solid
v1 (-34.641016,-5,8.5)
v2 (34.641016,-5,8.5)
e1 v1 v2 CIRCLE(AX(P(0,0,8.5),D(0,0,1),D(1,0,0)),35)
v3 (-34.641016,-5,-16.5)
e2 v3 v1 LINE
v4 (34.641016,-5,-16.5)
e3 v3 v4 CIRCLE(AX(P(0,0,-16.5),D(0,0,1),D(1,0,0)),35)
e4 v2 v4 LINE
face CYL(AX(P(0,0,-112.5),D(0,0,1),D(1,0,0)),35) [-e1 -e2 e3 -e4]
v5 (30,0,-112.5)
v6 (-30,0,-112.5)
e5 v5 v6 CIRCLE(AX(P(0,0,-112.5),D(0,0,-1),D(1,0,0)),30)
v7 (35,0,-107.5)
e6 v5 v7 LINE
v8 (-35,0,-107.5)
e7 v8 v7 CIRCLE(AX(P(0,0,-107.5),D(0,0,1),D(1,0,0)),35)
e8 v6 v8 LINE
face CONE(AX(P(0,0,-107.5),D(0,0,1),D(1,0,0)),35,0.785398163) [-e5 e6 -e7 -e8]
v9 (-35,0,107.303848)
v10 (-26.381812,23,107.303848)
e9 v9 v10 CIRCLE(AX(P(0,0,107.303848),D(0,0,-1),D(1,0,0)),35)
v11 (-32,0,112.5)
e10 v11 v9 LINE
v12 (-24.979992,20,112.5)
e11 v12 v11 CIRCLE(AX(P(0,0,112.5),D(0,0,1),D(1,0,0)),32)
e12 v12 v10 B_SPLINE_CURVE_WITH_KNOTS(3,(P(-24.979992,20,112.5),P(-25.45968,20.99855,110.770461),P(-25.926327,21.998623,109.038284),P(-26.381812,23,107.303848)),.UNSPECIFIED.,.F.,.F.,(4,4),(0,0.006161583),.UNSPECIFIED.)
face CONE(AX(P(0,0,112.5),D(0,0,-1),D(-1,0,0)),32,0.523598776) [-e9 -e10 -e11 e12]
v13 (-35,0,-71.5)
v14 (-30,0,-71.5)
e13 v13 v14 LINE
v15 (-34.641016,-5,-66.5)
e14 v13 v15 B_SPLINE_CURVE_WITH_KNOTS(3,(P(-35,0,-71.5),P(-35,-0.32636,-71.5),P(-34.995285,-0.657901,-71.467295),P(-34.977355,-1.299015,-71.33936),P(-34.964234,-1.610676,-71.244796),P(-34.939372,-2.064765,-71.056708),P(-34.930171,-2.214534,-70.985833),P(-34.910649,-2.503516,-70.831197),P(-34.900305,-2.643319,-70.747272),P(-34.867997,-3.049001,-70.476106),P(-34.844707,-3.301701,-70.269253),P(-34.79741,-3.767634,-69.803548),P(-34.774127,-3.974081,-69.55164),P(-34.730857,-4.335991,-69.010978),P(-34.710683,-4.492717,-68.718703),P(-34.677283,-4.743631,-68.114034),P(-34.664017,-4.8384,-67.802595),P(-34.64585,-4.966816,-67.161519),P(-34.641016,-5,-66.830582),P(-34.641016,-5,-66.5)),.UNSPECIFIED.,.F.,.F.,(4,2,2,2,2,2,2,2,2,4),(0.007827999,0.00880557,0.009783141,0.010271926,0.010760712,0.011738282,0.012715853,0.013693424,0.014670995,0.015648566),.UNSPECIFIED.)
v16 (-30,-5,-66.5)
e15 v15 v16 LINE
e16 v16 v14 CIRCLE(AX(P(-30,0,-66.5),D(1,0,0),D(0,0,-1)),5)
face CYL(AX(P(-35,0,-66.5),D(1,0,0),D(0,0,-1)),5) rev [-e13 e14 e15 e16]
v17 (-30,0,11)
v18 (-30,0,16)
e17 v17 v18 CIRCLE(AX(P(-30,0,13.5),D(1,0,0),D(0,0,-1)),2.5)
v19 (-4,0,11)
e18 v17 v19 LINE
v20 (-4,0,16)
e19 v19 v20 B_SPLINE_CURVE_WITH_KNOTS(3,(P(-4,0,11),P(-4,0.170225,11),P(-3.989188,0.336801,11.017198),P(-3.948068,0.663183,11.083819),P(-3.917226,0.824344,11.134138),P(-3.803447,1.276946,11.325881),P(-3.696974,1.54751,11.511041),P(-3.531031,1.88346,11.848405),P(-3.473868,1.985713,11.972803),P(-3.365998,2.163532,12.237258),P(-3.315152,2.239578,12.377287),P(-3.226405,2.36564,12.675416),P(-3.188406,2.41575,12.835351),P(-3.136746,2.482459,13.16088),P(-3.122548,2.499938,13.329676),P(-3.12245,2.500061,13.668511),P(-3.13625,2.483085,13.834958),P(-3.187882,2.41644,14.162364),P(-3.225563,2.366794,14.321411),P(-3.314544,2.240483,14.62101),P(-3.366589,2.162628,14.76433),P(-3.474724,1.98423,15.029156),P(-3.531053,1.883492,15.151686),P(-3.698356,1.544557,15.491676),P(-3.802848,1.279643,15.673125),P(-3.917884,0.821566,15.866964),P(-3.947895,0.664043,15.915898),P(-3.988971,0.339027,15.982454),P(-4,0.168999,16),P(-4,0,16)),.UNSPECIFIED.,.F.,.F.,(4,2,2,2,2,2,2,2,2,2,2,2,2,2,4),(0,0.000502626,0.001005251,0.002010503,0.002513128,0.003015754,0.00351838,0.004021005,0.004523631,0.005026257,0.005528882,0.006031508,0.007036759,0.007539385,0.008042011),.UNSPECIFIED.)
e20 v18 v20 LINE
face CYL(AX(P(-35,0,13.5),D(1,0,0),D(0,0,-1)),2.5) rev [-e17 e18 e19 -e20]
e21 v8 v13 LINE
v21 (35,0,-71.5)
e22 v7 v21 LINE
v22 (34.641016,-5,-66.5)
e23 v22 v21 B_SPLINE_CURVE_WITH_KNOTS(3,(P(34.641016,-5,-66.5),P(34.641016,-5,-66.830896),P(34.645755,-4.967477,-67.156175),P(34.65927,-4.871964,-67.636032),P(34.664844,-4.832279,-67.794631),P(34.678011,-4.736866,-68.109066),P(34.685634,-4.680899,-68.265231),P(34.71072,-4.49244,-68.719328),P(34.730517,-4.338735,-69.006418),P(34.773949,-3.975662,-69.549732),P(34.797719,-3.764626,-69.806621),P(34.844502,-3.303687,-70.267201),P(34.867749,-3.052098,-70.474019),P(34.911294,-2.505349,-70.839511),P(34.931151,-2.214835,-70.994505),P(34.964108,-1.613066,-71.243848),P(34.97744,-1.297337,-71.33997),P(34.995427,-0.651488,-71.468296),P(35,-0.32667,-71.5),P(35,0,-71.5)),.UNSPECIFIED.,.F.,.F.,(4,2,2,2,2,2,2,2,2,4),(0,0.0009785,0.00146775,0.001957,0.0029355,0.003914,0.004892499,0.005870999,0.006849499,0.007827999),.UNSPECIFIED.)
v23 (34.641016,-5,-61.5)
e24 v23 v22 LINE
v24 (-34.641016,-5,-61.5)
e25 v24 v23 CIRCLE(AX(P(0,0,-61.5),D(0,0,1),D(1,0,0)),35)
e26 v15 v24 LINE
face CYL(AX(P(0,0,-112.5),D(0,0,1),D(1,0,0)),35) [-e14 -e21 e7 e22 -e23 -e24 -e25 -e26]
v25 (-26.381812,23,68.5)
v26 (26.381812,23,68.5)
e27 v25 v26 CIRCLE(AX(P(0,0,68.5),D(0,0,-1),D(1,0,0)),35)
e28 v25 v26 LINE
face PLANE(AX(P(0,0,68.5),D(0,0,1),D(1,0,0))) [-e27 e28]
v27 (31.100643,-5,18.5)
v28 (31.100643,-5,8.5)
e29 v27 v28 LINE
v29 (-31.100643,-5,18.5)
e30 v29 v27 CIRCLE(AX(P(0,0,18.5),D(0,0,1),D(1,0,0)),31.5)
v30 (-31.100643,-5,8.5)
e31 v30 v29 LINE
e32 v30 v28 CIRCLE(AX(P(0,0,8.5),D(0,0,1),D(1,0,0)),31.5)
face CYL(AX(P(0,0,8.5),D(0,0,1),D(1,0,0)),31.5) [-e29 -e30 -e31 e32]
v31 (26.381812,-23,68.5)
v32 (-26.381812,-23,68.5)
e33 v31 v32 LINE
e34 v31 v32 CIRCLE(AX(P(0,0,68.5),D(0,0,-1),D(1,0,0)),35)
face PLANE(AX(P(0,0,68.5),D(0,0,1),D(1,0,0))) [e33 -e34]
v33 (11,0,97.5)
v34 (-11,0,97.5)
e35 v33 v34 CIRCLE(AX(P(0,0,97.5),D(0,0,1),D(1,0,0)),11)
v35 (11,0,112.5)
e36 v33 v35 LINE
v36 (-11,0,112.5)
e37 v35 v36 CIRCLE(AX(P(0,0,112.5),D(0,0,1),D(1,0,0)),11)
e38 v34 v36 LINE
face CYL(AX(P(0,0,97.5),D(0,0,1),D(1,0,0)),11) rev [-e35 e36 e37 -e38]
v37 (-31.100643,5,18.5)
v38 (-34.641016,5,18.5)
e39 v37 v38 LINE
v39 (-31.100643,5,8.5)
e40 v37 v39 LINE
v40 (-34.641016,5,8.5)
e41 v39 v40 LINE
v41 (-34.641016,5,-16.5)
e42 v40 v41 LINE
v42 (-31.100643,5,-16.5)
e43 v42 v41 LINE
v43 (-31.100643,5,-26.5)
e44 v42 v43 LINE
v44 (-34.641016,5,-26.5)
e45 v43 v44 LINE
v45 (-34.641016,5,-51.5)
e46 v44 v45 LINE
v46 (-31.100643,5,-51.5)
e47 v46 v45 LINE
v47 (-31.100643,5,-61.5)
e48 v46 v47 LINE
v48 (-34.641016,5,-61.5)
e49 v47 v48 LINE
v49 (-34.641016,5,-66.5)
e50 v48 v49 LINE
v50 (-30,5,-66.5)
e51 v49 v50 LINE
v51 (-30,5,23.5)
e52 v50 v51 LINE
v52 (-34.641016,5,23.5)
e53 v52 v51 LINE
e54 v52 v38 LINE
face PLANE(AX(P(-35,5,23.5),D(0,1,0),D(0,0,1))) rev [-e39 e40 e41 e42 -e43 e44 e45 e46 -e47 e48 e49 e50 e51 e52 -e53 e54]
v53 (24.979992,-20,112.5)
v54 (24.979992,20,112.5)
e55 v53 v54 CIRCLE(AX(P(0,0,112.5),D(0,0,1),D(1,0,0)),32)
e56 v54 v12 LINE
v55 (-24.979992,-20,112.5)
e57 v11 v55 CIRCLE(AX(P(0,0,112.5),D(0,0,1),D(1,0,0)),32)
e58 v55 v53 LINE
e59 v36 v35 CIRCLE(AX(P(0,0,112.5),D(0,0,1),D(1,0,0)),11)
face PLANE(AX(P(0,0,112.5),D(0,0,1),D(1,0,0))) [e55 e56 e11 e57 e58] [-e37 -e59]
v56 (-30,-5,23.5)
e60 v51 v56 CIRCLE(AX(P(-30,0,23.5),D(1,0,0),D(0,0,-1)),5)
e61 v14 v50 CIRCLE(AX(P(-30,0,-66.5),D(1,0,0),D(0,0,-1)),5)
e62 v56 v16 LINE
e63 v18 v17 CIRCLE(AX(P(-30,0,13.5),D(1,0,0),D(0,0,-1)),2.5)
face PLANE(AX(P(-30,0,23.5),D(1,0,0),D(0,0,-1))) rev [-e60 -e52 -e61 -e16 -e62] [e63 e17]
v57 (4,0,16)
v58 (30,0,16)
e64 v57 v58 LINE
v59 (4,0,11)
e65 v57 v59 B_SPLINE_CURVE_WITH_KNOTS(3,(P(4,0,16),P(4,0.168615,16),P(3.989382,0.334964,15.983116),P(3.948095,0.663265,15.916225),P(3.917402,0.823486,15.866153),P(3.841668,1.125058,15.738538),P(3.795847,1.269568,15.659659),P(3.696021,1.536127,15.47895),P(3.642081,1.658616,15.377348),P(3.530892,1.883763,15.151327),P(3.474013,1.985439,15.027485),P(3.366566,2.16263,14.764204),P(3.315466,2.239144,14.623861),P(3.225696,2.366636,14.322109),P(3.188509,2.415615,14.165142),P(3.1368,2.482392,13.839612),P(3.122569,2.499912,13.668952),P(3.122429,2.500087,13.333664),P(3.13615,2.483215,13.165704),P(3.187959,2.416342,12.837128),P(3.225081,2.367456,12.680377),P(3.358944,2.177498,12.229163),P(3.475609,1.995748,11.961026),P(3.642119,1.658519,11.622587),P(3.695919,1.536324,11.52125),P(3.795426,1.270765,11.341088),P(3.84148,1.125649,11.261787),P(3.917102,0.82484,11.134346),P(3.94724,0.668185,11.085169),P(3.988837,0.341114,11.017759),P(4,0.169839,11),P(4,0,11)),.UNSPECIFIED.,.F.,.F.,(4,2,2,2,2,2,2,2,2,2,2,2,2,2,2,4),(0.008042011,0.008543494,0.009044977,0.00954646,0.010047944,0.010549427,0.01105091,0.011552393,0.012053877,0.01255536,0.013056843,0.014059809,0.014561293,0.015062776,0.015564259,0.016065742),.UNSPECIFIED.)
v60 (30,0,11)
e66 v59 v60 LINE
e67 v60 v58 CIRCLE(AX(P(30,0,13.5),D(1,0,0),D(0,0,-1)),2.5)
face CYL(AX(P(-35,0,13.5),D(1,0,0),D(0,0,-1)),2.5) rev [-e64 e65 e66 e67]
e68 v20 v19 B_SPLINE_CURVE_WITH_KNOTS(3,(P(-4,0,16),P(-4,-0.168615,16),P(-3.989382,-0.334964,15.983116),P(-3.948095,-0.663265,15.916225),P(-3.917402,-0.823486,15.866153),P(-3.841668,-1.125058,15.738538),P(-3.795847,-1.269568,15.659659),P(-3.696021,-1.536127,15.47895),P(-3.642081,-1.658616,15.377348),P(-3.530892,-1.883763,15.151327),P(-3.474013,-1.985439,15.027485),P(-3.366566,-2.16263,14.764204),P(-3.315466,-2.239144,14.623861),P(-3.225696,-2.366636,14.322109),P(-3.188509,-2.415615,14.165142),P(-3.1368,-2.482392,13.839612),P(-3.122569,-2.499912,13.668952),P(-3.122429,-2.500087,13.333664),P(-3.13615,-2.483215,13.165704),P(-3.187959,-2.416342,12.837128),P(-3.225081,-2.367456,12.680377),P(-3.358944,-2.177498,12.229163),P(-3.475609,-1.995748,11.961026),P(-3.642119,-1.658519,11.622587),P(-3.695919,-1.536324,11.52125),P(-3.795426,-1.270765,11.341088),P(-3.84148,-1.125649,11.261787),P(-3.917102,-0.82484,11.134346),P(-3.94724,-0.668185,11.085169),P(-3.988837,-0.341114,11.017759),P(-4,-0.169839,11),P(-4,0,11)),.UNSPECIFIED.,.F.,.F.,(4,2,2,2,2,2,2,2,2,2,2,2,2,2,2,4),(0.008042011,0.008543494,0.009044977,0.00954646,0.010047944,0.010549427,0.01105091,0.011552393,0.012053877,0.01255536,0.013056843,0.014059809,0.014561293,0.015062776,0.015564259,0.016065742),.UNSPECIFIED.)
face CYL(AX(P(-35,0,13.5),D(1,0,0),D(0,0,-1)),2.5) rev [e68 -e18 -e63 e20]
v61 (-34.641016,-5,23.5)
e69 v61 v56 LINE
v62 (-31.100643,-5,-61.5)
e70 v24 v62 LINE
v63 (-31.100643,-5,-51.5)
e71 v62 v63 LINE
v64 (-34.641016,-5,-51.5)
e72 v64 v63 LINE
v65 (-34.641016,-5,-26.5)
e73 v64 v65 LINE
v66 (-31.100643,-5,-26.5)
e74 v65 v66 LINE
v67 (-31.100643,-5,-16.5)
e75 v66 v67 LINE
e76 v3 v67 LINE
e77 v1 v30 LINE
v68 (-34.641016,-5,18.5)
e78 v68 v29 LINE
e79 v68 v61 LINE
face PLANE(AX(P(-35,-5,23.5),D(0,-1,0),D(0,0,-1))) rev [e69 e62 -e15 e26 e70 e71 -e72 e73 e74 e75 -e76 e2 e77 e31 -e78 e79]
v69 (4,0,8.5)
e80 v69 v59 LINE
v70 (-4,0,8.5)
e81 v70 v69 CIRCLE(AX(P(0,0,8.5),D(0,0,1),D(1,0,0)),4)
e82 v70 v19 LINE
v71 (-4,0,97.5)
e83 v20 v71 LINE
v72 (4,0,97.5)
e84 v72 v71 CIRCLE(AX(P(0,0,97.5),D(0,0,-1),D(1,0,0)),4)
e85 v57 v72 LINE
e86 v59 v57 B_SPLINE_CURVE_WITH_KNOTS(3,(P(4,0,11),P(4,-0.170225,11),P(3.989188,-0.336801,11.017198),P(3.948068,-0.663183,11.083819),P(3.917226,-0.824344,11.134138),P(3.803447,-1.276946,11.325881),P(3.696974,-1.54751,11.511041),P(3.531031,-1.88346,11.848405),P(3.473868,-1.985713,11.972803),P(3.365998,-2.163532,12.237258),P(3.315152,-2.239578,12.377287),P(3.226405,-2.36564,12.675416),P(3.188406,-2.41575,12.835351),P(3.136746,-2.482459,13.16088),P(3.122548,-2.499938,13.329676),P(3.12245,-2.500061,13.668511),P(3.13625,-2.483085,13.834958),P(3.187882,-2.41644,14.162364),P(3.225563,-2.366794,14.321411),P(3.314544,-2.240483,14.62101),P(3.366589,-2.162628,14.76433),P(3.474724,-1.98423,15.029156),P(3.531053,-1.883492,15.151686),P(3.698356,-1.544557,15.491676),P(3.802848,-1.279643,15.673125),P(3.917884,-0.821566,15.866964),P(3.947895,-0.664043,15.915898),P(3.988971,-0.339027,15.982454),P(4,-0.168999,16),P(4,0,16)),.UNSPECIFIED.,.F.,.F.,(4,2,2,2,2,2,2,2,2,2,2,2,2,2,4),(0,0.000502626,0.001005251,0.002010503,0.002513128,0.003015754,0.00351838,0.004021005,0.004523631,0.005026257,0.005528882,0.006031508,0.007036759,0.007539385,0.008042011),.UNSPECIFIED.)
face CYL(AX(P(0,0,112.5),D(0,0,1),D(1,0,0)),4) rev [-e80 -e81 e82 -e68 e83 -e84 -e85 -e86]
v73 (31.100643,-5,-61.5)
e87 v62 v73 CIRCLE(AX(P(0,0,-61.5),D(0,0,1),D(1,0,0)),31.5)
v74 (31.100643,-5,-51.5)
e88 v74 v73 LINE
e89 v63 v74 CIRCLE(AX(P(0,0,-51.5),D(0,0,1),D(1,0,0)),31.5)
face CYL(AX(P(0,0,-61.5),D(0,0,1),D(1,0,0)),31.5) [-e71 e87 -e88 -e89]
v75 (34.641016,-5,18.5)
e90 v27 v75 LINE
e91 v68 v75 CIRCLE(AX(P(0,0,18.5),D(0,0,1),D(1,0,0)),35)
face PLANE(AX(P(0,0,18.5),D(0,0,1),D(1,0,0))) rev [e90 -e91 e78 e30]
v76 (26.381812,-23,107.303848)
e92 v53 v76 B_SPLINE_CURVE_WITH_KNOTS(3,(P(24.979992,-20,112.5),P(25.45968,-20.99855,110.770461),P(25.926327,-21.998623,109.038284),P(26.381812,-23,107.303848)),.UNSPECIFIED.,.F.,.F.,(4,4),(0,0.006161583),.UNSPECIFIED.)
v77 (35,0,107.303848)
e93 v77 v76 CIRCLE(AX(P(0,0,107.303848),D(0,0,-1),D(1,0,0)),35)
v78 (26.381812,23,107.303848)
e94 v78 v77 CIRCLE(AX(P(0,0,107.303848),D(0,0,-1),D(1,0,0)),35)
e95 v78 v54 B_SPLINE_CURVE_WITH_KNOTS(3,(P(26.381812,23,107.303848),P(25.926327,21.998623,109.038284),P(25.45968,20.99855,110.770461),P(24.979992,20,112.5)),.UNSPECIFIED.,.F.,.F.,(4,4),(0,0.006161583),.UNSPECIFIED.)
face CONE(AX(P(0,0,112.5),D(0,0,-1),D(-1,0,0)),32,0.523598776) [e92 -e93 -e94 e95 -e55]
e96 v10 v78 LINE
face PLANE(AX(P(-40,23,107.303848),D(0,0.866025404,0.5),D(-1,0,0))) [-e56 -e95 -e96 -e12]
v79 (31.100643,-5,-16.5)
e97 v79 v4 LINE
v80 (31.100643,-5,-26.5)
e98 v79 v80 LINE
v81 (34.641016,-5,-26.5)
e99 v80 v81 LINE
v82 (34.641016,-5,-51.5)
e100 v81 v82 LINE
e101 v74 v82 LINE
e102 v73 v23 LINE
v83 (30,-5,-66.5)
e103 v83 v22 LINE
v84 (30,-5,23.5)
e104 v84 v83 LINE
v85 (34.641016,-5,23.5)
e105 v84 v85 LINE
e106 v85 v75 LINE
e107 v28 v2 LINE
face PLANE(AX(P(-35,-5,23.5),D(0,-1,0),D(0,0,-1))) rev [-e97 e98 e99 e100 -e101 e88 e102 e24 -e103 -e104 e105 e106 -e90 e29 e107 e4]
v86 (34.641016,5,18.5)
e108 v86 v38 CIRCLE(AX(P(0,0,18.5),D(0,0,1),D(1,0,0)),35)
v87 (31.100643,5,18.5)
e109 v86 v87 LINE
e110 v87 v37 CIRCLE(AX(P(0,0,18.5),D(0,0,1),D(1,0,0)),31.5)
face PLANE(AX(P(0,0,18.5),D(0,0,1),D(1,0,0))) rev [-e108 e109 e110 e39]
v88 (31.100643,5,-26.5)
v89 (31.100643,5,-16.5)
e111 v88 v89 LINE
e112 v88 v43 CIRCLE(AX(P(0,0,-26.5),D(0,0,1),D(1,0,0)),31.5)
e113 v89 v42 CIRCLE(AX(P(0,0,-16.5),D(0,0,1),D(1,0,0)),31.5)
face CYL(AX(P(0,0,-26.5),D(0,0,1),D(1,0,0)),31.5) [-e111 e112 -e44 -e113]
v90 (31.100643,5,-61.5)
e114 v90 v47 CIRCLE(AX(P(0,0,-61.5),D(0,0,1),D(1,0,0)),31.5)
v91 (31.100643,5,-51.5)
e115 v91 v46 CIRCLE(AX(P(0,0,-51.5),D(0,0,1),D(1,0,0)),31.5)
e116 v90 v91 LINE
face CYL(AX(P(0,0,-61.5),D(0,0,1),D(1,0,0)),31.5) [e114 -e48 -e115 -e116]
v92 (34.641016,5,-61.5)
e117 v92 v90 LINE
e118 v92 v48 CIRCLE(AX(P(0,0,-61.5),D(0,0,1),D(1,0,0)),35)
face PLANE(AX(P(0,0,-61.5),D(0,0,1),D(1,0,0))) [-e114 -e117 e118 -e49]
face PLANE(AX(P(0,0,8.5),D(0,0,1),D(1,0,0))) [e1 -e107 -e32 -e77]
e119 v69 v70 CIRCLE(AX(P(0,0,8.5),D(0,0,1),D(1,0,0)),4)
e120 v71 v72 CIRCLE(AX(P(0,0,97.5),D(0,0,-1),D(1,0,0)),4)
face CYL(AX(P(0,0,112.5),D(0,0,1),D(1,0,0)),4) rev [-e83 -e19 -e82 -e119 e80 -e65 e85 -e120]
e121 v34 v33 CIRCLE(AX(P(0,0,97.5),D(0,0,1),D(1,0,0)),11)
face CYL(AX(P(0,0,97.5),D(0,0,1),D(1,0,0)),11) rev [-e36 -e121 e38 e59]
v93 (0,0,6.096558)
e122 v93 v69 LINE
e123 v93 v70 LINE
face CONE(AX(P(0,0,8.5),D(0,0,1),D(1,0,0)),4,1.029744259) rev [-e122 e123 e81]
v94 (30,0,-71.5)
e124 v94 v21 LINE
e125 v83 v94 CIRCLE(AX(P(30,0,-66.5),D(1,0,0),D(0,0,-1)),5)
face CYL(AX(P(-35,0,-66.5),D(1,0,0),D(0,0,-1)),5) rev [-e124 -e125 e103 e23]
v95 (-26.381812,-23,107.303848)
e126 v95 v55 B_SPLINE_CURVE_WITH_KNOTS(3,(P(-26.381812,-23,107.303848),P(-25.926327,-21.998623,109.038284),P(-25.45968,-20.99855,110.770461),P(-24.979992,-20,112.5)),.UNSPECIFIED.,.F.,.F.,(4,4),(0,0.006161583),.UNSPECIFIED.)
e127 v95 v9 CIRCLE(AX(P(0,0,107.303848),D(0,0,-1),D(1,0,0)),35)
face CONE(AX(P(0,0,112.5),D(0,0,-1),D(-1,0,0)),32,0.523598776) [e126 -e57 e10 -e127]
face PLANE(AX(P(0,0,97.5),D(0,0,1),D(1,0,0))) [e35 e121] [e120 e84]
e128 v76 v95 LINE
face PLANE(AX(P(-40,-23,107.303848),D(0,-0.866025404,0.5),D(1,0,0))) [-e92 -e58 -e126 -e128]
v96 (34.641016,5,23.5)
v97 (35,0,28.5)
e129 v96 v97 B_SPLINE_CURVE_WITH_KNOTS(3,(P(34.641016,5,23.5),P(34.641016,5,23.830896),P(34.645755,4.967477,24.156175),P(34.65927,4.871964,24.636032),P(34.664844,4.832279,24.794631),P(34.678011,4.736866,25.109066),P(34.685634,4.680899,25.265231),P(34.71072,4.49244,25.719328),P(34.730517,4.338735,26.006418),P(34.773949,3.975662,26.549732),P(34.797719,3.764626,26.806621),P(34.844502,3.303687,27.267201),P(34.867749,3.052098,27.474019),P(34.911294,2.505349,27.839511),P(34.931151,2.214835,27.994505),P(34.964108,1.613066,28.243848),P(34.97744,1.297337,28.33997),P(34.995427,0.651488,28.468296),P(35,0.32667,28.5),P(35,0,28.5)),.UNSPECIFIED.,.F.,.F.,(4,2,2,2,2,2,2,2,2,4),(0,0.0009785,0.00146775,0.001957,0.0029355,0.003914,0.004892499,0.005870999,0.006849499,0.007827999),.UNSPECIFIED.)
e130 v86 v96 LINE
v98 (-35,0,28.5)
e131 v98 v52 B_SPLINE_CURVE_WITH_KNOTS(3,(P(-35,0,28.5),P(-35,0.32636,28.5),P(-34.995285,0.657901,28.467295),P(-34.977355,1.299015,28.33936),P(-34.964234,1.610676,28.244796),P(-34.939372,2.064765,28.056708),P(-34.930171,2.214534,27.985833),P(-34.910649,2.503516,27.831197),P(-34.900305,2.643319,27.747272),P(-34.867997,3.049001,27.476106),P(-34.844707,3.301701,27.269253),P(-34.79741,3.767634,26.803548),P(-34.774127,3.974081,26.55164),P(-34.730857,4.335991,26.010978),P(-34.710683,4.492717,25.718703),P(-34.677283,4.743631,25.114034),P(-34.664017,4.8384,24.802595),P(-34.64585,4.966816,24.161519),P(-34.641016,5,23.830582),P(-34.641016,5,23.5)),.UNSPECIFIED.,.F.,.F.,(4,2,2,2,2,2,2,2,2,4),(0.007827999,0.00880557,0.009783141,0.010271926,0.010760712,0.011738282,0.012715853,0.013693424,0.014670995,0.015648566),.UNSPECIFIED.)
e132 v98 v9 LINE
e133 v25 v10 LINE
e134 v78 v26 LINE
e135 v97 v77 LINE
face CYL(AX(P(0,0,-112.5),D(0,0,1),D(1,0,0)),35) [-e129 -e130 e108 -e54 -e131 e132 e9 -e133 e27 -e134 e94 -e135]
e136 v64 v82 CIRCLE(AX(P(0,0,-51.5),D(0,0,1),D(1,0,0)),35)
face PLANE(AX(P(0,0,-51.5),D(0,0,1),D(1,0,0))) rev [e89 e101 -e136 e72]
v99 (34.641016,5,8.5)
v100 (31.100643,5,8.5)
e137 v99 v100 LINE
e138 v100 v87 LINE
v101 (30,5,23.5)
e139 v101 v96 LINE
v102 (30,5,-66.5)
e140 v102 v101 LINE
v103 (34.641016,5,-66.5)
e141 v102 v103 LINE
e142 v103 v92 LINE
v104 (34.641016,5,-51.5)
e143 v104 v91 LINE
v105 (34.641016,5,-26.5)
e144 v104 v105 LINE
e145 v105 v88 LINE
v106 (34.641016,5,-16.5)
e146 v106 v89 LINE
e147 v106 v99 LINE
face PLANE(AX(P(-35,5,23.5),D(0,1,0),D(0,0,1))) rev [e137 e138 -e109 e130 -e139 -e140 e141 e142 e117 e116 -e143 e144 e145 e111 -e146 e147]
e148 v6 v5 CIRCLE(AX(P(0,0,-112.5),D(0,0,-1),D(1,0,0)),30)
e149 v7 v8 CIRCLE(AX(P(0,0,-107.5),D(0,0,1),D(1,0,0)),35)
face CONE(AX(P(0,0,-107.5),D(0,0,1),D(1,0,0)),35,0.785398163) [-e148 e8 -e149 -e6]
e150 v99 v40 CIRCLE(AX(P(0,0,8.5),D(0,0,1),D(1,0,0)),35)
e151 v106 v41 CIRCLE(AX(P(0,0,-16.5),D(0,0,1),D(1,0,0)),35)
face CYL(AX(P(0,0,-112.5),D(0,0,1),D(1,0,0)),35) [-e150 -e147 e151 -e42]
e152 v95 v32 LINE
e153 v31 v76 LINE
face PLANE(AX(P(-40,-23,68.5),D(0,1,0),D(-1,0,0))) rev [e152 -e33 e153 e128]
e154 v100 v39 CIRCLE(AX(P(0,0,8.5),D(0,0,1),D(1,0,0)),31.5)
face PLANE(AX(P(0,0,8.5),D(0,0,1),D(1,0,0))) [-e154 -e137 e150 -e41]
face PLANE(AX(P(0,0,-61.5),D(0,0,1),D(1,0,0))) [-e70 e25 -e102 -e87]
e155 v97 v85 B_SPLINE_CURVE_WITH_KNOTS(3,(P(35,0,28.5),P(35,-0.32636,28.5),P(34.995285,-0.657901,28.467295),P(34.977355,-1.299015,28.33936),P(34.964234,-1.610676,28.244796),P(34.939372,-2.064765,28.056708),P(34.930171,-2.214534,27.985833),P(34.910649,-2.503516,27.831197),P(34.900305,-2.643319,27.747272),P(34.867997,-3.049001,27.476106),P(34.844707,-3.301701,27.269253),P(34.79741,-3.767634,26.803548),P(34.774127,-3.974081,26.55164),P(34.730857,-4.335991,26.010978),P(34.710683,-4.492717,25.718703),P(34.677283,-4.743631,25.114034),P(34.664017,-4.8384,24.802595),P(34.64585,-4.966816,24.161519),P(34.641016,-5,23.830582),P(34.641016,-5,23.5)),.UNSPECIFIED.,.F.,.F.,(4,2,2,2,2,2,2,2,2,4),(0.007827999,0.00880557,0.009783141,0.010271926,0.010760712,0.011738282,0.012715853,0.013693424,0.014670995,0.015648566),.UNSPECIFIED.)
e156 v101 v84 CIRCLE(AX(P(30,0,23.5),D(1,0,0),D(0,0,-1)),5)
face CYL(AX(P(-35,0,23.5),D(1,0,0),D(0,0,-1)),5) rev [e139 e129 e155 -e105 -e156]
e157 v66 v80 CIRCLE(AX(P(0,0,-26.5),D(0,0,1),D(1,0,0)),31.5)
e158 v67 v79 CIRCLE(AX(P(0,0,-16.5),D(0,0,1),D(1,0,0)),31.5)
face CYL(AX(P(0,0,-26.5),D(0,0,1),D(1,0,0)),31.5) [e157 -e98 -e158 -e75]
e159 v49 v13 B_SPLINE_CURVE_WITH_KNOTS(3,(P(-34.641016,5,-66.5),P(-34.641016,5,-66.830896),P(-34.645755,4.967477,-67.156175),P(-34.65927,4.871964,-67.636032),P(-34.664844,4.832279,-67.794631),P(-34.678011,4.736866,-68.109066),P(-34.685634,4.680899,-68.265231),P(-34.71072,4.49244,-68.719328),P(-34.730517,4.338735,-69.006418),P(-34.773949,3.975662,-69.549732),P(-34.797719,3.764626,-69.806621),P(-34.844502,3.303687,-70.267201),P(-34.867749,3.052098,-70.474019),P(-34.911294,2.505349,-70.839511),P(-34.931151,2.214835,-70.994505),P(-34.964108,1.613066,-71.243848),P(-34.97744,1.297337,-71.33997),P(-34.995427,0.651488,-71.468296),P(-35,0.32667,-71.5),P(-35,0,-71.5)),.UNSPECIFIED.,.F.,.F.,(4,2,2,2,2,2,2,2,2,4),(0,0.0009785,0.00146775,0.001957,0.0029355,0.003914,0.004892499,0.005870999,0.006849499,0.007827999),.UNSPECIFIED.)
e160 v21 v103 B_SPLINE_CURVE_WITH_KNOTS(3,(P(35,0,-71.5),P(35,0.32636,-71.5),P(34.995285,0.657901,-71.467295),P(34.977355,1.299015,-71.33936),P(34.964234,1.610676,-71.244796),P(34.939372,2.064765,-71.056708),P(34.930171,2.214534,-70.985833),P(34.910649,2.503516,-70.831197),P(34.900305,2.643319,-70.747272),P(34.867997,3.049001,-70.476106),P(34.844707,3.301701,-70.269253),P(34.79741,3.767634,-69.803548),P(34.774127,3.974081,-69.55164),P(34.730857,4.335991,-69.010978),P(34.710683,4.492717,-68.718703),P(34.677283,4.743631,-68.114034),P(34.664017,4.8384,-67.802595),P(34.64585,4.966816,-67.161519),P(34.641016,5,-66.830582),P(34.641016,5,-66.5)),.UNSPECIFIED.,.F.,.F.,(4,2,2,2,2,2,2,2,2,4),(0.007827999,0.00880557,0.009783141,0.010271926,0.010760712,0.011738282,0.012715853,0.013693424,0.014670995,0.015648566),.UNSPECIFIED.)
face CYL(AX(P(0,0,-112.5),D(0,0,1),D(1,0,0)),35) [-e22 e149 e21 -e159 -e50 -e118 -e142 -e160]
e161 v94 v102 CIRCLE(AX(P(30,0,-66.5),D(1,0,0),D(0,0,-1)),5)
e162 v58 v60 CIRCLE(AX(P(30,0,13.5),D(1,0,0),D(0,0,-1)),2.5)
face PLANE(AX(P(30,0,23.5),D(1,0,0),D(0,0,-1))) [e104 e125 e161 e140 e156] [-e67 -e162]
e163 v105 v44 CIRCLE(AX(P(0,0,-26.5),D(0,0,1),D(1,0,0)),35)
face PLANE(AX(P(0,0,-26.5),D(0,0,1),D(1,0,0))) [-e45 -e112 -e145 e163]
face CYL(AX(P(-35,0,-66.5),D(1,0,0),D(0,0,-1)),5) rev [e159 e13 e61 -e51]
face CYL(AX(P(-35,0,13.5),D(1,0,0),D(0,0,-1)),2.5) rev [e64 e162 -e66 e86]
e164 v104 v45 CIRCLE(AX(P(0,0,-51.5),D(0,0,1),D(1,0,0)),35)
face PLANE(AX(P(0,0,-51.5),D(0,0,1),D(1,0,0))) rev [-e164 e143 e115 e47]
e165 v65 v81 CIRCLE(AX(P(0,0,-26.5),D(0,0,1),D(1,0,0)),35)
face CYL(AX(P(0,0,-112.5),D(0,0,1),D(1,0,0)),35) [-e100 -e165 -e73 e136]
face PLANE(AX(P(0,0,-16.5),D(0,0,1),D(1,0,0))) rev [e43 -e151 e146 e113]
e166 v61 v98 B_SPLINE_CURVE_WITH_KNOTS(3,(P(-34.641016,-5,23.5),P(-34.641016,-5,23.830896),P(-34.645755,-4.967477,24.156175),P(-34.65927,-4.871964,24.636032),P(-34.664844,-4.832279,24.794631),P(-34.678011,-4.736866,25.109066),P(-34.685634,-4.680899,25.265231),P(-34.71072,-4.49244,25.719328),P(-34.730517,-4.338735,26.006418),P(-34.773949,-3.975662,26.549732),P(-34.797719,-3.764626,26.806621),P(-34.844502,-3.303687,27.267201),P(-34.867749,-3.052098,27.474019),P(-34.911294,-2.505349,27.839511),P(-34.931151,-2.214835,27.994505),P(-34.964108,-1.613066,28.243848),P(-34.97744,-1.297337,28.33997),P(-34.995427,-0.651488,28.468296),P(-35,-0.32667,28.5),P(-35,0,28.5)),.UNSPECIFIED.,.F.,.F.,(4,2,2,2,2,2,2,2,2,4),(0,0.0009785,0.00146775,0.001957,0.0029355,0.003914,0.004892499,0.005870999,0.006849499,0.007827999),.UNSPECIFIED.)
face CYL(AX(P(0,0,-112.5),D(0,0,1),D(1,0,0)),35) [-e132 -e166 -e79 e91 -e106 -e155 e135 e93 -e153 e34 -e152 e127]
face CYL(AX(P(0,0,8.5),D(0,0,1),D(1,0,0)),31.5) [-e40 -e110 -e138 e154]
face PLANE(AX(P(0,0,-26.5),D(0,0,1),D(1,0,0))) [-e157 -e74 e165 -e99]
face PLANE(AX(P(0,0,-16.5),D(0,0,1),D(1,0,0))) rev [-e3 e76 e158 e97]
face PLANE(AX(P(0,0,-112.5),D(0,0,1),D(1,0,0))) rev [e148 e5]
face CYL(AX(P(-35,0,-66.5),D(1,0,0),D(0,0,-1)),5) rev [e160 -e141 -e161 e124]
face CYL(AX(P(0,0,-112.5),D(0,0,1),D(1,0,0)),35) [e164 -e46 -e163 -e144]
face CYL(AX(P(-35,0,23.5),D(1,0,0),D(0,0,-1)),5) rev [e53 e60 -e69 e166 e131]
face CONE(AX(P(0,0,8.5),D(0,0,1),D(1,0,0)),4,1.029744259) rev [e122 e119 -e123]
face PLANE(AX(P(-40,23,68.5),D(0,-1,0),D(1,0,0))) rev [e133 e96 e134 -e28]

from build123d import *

# Parameters (mm, degrees)
SKETCH1_R                  = 35
BOSS_EXTRUDE1_DEPTH        = 112.5
SKETCH2_R                  = 35
SKETCH2_R_2                = 31.5
CUT_EXTRUDE1_DEPTH         = 5
LINEAR_PATTERN1_COUNT      = 2
LINEAR_PATTERN1_PITCH      = 35
LINEAR_PATTERN1_COL_COUNT  = 2
LINEAR_PATTERN1_COL_PITCH  = 35
CUT_EXTRUDE2_DEPTH         = 123.907485533
CUT_EXTRUDE2_DEPTH_BACK    = 123.907485533
BOSS_EXTRUDE2_DEPTH        = 30
CUT_EXTRUDE3_DEPTH         = 123.907485681
CUT_EXTRUDE3_DEPTH_BACK    = 123.907485681
SKETCH4_R                  = 2.5
CHAMFERC5_SIZE             = 5
CHAMFER3_30DEG_SIZE        = 3
CHAMFER3_30DEG_SIZE2       = 5.196152423
SKETCH5_W                  = 80
SKETCH5_H                  = 17
CUT_LEFT_PLANE_DEPTH       = 44
CHAMFER3_SIZE              = 3
CHAMFER3_SIZE2             = 5.196152423
M10X1_0_TAPPED_HOLE1_D     = 8
M10X1_0_TAPPED_HOLE1_DEPTH = 104
M10X1_0_TAPPED_HOLE1_TIP   = 2.403442476
SKETCH8_R                  = 11
CUT_EXTRUDE5_DEPTH         = 15


with BuildPart() as part:
    # Sketch1 → Boss-Extrude1 (new, symmetric)
    with BuildSketch(Plane.XY):
        Circle(SKETCH1_R)
    extrude(amount=BOSS_EXTRUDE1_DEPTH, both=True)

    # Sketch2 → Cut-Extrude1 (cut, symmetric)
    with BuildSketch(Plane.XY.offset(-21.5)):
        Circle(SKETCH2_R)
        Circle(SKETCH2_R_2, mode=Mode.SUBTRACT)
    cut_extrude1 = extrude(amount=CUT_EXTRUDE1_DEPTH, both=True, mode=Mode.SUBTRACT)

    # Linear pattern1: Cut-Extrude1 ×2
    with Locations(*[(0, 0, -i * LINEAR_PATTERN1_PITCH) for i in range(1, LINEAR_PATTERN1_COUNT)]):
        add(cut_extrude1, mode=Mode.SUBTRACT)

    # Linear pattern1 col: Cut-Extrude1 ×2
    with Locations(*[(0, 0, i * LINEAR_PATTERN1_COL_PITCH) for i in range(1, LINEAR_PATTERN1_COL_COUNT)]):
        add(cut_extrude1, mode=Mode.SUBTRACT)

    # Sketch3<2> → Cut-Extrude2 (cut, two sides: drawn at the far end of the back side and taken through both)
    with BuildSketch(Plane(origin=(0, 0, 0), x_dir=(0, 0, -1), z_dir=(1, 0, 0)).offset(-CUT_EXTRUDE2_DEPTH_BACK)):
        with BuildLine():
            Line((-23.5, 5), (66.5, 5))
            ThreePointArc((66.5, 5), (71.5, 0), (66.5, -5))
            Line((66.5, -5), (-23.5, -5))
            ThreePointArc((-23.5, -5), (-28.5, 0), (-23.5, 5))
        make_face()
    extrude(amount=CUT_EXTRUDE2_DEPTH + CUT_EXTRUDE2_DEPTH_BACK, mode=Mode.SUBTRACT)

    # 草图3<2> → Boss-Extrude2 (add, symmetric)
    with BuildSketch(Plane(origin=(0, 0, 0), x_dir=(0, 0, -1), z_dir=(1, 0, 0))):
        with BuildLine():
            Line((-23.5, 5), (66.5, 5))
            ThreePointArc((66.5, 5), (71.5, 0), (66.5, -5))
            Line((66.5, -5), (-23.5, -5))
            ThreePointArc((-23.5, -5), (-28.5, 0), (-23.5, 5))
        make_face()
    extrude(amount=BOSS_EXTRUDE2_DEPTH, both=True)

    # Sketch4 → Cut-Extrude3 (cut, two sides: drawn at the far end of the back side and taken through both)
    with BuildSketch(Plane(origin=(0, 0, 0), x_dir=(0, 0, -1), z_dir=(1, 0, 0)).offset(-CUT_EXTRUDE3_DEPTH_BACK)):
        with Locations((-13.5, 0)):
            Circle(SKETCH4_R)
    extrude(amount=CUT_EXTRUDE3_DEPTH + CUT_EXTRUDE3_DEPTH_BACK, mode=Mode.SUBTRACT)

    # ChamferC5
    chamferc5_edges = [part.edges().sort_by_distance(p)[0] for p in [
        (-35, 0, -112.5),
    ]]
    chamfer(chamferc5_edges, length=CHAMFERC5_SIZE)

    # Chamfer3-30deg
    chamfer3_30deg_edges = [part.edges().sort_by_distance(p)[0] for p in [
        (-35, 0, 112.5),
    ]]
    chamfer3_30deg_side = [part.faces().sort_by_distance(p)[0] for p in [
        (0, 0, 112.5),
    ]]
    chamfer(chamfer3_30deg_edges, length=CHAMFER3_30DEG_SIZE, length2=CHAMFER3_30DEG_SIZE2, reference=chamfer3_30deg_side[0])

    # Sketch5 → Cut-Left Plane (cut)
    with BuildSketch(Plane.XY.offset(112.5)):
        with Locations((0, 31.5)):
            Rectangle(SKETCH5_W, SKETCH5_H)
        with Locations((0, -31.5)):
            Rectangle(SKETCH5_W, SKETCH5_H)
    extrude(amount=-CUT_LEFT_PLANE_DEPTH, mode=Mode.SUBTRACT)

    # Chamfer3
    chamfer3_edges = [part.edges().sort_by_distance(p)[0] for p in [
        (0, -23, 112.5),
        (0, 23, 112.5),
    ]]
    chamfer3_side = [part.faces().sort_by_distance(p)[0] for p in [
        (0, 0, 112.5),
    ]]
    chamfer(chamfer3_edges, length=CHAMFER3_SIZE, length2=CHAMFER3_SIZE2, reference=chamfer3_side[0])

    # M10x1.0 Tapped Hole1
    with Locations(Plane.XY.offset(112.5)):
        with Locations((0, 0)):
            Hole(M10X1_0_TAPPED_HOLE1_D / 2, depth=M10X1_0_TAPPED_HOLE1_DEPTH)
            with Locations((0, 0, -(M10X1_0_TAPPED_HOLE1_DEPTH + M10X1_0_TAPPED_HOLE1_TIP / 2))):  # 118° drill point
                Cone(0, M10X1_0_TAPPED_HOLE1_D / 2, M10X1_0_TAPPED_HOLE1_TIP, mode=Mode.SUBTRACT)

    # Sketch8 → Cut-Extrude5 (cut)
    with BuildSketch(Plane.XY.offset(112.5)):
        Circle(SKETCH8_R)
    extrude(amount=-CUT_EXTRUDE5_DEPTH, mode=Mode.SUBTRACT)


solid = part.part
